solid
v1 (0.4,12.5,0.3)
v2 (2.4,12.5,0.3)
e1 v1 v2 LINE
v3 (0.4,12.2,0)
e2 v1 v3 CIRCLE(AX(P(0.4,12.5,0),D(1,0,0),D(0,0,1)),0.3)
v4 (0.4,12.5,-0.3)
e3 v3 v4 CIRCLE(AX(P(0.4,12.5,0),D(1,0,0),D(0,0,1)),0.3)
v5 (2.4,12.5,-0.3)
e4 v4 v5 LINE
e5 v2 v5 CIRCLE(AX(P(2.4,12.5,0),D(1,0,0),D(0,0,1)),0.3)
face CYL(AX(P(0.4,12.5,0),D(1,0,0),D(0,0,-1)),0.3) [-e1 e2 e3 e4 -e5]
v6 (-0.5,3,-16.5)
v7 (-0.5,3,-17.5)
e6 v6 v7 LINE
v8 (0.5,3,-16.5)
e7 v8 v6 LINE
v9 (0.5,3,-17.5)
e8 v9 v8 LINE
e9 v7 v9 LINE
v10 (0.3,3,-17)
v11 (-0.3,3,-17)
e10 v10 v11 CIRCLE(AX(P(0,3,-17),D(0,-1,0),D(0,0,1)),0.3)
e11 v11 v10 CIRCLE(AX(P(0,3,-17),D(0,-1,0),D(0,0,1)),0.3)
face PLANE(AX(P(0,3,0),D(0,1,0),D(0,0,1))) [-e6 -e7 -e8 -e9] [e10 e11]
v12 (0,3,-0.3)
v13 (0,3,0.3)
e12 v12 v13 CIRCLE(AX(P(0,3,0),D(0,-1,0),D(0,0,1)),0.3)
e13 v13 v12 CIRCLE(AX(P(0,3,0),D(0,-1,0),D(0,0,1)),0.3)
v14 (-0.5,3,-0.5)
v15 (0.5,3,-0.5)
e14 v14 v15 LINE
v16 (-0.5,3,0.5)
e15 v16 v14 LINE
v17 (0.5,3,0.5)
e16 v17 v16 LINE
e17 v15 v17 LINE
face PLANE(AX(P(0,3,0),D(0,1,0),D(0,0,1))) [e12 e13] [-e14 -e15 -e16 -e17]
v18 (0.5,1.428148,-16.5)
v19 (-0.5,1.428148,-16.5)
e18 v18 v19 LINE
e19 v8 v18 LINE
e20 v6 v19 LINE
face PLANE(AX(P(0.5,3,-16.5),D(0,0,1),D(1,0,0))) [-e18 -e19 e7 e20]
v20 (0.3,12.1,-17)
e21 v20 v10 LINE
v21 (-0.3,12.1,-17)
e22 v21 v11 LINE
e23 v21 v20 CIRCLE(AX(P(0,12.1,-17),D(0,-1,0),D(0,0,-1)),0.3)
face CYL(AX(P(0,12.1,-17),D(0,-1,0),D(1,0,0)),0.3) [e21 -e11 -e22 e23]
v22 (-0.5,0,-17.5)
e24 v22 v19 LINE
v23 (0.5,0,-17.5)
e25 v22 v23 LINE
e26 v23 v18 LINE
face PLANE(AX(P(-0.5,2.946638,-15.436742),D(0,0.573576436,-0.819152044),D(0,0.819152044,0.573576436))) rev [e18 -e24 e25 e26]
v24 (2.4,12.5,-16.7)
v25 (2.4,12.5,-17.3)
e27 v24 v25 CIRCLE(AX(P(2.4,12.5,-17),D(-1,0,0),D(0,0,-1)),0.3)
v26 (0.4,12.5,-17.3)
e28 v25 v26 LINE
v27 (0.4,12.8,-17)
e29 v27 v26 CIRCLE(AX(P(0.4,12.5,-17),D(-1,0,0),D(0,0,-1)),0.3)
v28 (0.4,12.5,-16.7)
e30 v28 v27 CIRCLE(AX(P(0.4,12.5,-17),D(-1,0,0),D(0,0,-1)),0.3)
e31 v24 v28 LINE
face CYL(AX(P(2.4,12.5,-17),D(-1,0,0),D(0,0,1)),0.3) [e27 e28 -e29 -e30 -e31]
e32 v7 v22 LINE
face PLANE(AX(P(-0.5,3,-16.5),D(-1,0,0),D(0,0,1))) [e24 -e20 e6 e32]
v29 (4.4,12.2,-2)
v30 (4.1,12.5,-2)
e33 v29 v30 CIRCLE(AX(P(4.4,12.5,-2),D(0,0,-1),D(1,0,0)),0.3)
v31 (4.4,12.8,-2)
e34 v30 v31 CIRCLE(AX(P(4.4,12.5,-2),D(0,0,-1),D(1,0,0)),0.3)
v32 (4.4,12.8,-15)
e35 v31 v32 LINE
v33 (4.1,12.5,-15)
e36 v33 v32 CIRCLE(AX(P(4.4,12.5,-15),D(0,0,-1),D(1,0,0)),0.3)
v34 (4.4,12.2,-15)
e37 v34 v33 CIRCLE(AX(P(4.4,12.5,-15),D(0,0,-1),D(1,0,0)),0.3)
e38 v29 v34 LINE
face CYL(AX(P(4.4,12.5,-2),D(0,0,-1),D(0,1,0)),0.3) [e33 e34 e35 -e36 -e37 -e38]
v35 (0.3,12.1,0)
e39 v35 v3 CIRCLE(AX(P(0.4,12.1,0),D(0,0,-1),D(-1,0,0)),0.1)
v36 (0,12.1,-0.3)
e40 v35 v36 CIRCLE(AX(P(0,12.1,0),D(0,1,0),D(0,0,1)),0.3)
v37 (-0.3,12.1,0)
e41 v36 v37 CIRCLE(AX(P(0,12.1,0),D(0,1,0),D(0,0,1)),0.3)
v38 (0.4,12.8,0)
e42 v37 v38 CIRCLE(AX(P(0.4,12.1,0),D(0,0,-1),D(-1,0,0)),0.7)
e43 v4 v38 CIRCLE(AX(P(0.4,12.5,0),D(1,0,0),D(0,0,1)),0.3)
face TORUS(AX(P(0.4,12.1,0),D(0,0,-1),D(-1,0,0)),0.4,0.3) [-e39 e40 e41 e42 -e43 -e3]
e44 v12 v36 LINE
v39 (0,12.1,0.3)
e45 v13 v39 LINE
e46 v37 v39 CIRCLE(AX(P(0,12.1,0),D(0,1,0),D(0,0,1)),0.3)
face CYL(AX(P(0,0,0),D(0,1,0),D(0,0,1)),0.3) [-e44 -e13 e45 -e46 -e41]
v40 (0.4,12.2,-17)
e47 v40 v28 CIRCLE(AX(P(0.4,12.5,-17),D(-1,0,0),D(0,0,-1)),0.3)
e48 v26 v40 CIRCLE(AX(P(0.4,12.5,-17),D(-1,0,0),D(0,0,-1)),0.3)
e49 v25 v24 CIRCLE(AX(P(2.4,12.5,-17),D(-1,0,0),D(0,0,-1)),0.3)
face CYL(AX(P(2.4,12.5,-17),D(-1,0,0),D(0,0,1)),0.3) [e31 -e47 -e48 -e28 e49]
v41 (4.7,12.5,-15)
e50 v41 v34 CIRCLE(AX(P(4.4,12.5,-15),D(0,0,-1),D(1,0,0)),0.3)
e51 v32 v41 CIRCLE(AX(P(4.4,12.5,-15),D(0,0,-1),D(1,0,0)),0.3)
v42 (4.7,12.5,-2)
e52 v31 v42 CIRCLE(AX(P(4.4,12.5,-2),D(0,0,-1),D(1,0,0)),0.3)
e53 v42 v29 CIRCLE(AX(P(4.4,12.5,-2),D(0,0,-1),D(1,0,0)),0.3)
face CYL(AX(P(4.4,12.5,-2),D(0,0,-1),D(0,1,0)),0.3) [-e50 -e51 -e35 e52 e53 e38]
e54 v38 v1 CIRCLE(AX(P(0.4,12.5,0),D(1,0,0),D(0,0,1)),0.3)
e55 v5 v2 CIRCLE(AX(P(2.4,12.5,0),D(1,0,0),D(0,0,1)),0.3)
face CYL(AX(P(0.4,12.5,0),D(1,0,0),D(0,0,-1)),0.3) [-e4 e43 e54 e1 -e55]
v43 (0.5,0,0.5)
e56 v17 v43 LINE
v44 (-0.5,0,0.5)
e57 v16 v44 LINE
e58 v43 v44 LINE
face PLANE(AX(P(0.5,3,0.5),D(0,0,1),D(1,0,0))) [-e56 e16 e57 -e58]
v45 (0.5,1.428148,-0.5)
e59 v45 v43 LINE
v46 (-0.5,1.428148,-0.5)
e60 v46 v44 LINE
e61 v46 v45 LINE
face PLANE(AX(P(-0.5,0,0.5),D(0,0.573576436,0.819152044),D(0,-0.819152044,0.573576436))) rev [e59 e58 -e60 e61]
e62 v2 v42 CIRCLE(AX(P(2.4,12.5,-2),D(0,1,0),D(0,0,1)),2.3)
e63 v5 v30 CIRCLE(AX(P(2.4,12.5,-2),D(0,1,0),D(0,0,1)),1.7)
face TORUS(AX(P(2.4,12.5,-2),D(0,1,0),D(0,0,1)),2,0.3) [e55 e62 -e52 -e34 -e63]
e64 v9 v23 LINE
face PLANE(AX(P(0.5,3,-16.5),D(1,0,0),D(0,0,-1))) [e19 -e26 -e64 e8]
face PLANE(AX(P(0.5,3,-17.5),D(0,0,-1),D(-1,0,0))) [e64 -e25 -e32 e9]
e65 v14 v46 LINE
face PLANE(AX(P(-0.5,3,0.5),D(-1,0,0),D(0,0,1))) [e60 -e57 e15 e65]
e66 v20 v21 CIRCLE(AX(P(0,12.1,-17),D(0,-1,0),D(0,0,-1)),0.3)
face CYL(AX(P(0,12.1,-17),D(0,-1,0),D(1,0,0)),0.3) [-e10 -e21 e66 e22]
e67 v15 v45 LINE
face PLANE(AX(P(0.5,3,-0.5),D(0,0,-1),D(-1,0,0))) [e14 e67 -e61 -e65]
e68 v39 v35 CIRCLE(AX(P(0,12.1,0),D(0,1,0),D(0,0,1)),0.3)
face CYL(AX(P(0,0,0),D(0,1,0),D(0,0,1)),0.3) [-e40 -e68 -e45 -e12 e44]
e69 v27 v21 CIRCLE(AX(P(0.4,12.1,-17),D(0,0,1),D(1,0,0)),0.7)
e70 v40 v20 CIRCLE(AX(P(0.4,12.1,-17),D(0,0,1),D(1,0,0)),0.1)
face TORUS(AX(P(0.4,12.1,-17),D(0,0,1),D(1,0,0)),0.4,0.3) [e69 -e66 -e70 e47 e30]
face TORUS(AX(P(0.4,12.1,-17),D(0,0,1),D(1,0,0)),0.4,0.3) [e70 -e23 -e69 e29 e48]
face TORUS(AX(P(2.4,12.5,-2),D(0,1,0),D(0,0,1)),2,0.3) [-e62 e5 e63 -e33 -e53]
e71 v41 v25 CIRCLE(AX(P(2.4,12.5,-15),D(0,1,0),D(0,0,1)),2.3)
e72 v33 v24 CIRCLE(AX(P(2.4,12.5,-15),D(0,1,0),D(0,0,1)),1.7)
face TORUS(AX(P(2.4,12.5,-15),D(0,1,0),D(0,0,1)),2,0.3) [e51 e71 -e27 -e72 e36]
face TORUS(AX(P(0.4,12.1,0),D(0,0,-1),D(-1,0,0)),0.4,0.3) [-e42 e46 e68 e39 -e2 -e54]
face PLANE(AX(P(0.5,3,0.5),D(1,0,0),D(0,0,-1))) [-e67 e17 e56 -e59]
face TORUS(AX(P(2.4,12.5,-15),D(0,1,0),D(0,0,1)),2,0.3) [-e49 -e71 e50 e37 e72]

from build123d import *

# Parameters (mm, degrees)
SKETCH2_R               = 0.3
SKETCH4_W               = 1
SKETCH4_H               = 1
BOSS_EXTRUDE1_DEPTH     = 3
CUT_EXTRUDE1_DEPTH      = 23.185130234
CUT_EXTRUDE1_DEPTH_BACK = 23.185130234


with BuildPart() as part:
    # Sweep1: sweep along a curve in space
    with BuildLine() as sweep1_path:
        Line((0, 0, 0), (0, 12.1, 0))
        ThreePointArc((0, 12.1, 0), (0.117157288, 12.382842712, 0), (0.4, 12.5, 0))
        Line((0.4, 12.5, 0), (2.4, 12.5, 0))
        ThreePointArc((2.4, 12.5, 0), (3.814213562, 12.5, -0.585786438), (4.4, 12.5, -2))
        Line((4.4, 12.5, -2), (4.4, 12.5, -15))
        ThreePointArc((4.4, 12.5, -15), (3.814213562, 12.5, -16.414213562), (2.4, 12.5, -17))
        Line((2.4, 12.5, -17), (0.4, 12.5, -17))
        ThreePointArc((0.4, 12.5, -17), (0.117157288, 12.382842712, -17), (0, 12.1, -17))
        Line((0, 12.1, -17), (0, 0, -17))
    # Sketch2 → Sweep1 (sweep)
    with BuildSketch(Plane(origin=(0, 0, 0), x_dir=(1, 0, 0), z_dir=(0, 1, 0))):
        Circle(SKETCH2_R)
    sweep(path=sweep1_path.line)

    # Sketch4 → Boss-Extrude1 (add)
    with BuildSketch(Plane(origin=(0, 0, 0), x_dir=(-1, 0, 0), z_dir=(0, -1, 0))):
        with Locations((0, 17)):
            Rectangle(SKETCH4_W, SKETCH4_H)
        Rectangle(SKETCH4_W, SKETCH4_H)
    extrude(amount=-BOSS_EXTRUDE1_DEPTH)

    # Sketch5 → Cut-Extrude1 (cut, two sides: drawn at the far end of the back side and taken through both)
    with BuildSketch(Plane(origin=(0, 0, 0), x_dir=(0, 0, -1), z_dir=(1, 0, 0)).offset(-CUT_EXTRUDE1_DEPTH_BACK)):
        Polygon((-0.5, 0), (1.563257824, 2.946637548), (15.436742176, 2.946637548), (17.5, 0), align=None)
    extrude(amount=CUT_EXTRUDE1_DEPTH + CUT_EXTRUDE1_DEPTH_BACK, mode=Mode.SUBTRACT)


solid = part.part
